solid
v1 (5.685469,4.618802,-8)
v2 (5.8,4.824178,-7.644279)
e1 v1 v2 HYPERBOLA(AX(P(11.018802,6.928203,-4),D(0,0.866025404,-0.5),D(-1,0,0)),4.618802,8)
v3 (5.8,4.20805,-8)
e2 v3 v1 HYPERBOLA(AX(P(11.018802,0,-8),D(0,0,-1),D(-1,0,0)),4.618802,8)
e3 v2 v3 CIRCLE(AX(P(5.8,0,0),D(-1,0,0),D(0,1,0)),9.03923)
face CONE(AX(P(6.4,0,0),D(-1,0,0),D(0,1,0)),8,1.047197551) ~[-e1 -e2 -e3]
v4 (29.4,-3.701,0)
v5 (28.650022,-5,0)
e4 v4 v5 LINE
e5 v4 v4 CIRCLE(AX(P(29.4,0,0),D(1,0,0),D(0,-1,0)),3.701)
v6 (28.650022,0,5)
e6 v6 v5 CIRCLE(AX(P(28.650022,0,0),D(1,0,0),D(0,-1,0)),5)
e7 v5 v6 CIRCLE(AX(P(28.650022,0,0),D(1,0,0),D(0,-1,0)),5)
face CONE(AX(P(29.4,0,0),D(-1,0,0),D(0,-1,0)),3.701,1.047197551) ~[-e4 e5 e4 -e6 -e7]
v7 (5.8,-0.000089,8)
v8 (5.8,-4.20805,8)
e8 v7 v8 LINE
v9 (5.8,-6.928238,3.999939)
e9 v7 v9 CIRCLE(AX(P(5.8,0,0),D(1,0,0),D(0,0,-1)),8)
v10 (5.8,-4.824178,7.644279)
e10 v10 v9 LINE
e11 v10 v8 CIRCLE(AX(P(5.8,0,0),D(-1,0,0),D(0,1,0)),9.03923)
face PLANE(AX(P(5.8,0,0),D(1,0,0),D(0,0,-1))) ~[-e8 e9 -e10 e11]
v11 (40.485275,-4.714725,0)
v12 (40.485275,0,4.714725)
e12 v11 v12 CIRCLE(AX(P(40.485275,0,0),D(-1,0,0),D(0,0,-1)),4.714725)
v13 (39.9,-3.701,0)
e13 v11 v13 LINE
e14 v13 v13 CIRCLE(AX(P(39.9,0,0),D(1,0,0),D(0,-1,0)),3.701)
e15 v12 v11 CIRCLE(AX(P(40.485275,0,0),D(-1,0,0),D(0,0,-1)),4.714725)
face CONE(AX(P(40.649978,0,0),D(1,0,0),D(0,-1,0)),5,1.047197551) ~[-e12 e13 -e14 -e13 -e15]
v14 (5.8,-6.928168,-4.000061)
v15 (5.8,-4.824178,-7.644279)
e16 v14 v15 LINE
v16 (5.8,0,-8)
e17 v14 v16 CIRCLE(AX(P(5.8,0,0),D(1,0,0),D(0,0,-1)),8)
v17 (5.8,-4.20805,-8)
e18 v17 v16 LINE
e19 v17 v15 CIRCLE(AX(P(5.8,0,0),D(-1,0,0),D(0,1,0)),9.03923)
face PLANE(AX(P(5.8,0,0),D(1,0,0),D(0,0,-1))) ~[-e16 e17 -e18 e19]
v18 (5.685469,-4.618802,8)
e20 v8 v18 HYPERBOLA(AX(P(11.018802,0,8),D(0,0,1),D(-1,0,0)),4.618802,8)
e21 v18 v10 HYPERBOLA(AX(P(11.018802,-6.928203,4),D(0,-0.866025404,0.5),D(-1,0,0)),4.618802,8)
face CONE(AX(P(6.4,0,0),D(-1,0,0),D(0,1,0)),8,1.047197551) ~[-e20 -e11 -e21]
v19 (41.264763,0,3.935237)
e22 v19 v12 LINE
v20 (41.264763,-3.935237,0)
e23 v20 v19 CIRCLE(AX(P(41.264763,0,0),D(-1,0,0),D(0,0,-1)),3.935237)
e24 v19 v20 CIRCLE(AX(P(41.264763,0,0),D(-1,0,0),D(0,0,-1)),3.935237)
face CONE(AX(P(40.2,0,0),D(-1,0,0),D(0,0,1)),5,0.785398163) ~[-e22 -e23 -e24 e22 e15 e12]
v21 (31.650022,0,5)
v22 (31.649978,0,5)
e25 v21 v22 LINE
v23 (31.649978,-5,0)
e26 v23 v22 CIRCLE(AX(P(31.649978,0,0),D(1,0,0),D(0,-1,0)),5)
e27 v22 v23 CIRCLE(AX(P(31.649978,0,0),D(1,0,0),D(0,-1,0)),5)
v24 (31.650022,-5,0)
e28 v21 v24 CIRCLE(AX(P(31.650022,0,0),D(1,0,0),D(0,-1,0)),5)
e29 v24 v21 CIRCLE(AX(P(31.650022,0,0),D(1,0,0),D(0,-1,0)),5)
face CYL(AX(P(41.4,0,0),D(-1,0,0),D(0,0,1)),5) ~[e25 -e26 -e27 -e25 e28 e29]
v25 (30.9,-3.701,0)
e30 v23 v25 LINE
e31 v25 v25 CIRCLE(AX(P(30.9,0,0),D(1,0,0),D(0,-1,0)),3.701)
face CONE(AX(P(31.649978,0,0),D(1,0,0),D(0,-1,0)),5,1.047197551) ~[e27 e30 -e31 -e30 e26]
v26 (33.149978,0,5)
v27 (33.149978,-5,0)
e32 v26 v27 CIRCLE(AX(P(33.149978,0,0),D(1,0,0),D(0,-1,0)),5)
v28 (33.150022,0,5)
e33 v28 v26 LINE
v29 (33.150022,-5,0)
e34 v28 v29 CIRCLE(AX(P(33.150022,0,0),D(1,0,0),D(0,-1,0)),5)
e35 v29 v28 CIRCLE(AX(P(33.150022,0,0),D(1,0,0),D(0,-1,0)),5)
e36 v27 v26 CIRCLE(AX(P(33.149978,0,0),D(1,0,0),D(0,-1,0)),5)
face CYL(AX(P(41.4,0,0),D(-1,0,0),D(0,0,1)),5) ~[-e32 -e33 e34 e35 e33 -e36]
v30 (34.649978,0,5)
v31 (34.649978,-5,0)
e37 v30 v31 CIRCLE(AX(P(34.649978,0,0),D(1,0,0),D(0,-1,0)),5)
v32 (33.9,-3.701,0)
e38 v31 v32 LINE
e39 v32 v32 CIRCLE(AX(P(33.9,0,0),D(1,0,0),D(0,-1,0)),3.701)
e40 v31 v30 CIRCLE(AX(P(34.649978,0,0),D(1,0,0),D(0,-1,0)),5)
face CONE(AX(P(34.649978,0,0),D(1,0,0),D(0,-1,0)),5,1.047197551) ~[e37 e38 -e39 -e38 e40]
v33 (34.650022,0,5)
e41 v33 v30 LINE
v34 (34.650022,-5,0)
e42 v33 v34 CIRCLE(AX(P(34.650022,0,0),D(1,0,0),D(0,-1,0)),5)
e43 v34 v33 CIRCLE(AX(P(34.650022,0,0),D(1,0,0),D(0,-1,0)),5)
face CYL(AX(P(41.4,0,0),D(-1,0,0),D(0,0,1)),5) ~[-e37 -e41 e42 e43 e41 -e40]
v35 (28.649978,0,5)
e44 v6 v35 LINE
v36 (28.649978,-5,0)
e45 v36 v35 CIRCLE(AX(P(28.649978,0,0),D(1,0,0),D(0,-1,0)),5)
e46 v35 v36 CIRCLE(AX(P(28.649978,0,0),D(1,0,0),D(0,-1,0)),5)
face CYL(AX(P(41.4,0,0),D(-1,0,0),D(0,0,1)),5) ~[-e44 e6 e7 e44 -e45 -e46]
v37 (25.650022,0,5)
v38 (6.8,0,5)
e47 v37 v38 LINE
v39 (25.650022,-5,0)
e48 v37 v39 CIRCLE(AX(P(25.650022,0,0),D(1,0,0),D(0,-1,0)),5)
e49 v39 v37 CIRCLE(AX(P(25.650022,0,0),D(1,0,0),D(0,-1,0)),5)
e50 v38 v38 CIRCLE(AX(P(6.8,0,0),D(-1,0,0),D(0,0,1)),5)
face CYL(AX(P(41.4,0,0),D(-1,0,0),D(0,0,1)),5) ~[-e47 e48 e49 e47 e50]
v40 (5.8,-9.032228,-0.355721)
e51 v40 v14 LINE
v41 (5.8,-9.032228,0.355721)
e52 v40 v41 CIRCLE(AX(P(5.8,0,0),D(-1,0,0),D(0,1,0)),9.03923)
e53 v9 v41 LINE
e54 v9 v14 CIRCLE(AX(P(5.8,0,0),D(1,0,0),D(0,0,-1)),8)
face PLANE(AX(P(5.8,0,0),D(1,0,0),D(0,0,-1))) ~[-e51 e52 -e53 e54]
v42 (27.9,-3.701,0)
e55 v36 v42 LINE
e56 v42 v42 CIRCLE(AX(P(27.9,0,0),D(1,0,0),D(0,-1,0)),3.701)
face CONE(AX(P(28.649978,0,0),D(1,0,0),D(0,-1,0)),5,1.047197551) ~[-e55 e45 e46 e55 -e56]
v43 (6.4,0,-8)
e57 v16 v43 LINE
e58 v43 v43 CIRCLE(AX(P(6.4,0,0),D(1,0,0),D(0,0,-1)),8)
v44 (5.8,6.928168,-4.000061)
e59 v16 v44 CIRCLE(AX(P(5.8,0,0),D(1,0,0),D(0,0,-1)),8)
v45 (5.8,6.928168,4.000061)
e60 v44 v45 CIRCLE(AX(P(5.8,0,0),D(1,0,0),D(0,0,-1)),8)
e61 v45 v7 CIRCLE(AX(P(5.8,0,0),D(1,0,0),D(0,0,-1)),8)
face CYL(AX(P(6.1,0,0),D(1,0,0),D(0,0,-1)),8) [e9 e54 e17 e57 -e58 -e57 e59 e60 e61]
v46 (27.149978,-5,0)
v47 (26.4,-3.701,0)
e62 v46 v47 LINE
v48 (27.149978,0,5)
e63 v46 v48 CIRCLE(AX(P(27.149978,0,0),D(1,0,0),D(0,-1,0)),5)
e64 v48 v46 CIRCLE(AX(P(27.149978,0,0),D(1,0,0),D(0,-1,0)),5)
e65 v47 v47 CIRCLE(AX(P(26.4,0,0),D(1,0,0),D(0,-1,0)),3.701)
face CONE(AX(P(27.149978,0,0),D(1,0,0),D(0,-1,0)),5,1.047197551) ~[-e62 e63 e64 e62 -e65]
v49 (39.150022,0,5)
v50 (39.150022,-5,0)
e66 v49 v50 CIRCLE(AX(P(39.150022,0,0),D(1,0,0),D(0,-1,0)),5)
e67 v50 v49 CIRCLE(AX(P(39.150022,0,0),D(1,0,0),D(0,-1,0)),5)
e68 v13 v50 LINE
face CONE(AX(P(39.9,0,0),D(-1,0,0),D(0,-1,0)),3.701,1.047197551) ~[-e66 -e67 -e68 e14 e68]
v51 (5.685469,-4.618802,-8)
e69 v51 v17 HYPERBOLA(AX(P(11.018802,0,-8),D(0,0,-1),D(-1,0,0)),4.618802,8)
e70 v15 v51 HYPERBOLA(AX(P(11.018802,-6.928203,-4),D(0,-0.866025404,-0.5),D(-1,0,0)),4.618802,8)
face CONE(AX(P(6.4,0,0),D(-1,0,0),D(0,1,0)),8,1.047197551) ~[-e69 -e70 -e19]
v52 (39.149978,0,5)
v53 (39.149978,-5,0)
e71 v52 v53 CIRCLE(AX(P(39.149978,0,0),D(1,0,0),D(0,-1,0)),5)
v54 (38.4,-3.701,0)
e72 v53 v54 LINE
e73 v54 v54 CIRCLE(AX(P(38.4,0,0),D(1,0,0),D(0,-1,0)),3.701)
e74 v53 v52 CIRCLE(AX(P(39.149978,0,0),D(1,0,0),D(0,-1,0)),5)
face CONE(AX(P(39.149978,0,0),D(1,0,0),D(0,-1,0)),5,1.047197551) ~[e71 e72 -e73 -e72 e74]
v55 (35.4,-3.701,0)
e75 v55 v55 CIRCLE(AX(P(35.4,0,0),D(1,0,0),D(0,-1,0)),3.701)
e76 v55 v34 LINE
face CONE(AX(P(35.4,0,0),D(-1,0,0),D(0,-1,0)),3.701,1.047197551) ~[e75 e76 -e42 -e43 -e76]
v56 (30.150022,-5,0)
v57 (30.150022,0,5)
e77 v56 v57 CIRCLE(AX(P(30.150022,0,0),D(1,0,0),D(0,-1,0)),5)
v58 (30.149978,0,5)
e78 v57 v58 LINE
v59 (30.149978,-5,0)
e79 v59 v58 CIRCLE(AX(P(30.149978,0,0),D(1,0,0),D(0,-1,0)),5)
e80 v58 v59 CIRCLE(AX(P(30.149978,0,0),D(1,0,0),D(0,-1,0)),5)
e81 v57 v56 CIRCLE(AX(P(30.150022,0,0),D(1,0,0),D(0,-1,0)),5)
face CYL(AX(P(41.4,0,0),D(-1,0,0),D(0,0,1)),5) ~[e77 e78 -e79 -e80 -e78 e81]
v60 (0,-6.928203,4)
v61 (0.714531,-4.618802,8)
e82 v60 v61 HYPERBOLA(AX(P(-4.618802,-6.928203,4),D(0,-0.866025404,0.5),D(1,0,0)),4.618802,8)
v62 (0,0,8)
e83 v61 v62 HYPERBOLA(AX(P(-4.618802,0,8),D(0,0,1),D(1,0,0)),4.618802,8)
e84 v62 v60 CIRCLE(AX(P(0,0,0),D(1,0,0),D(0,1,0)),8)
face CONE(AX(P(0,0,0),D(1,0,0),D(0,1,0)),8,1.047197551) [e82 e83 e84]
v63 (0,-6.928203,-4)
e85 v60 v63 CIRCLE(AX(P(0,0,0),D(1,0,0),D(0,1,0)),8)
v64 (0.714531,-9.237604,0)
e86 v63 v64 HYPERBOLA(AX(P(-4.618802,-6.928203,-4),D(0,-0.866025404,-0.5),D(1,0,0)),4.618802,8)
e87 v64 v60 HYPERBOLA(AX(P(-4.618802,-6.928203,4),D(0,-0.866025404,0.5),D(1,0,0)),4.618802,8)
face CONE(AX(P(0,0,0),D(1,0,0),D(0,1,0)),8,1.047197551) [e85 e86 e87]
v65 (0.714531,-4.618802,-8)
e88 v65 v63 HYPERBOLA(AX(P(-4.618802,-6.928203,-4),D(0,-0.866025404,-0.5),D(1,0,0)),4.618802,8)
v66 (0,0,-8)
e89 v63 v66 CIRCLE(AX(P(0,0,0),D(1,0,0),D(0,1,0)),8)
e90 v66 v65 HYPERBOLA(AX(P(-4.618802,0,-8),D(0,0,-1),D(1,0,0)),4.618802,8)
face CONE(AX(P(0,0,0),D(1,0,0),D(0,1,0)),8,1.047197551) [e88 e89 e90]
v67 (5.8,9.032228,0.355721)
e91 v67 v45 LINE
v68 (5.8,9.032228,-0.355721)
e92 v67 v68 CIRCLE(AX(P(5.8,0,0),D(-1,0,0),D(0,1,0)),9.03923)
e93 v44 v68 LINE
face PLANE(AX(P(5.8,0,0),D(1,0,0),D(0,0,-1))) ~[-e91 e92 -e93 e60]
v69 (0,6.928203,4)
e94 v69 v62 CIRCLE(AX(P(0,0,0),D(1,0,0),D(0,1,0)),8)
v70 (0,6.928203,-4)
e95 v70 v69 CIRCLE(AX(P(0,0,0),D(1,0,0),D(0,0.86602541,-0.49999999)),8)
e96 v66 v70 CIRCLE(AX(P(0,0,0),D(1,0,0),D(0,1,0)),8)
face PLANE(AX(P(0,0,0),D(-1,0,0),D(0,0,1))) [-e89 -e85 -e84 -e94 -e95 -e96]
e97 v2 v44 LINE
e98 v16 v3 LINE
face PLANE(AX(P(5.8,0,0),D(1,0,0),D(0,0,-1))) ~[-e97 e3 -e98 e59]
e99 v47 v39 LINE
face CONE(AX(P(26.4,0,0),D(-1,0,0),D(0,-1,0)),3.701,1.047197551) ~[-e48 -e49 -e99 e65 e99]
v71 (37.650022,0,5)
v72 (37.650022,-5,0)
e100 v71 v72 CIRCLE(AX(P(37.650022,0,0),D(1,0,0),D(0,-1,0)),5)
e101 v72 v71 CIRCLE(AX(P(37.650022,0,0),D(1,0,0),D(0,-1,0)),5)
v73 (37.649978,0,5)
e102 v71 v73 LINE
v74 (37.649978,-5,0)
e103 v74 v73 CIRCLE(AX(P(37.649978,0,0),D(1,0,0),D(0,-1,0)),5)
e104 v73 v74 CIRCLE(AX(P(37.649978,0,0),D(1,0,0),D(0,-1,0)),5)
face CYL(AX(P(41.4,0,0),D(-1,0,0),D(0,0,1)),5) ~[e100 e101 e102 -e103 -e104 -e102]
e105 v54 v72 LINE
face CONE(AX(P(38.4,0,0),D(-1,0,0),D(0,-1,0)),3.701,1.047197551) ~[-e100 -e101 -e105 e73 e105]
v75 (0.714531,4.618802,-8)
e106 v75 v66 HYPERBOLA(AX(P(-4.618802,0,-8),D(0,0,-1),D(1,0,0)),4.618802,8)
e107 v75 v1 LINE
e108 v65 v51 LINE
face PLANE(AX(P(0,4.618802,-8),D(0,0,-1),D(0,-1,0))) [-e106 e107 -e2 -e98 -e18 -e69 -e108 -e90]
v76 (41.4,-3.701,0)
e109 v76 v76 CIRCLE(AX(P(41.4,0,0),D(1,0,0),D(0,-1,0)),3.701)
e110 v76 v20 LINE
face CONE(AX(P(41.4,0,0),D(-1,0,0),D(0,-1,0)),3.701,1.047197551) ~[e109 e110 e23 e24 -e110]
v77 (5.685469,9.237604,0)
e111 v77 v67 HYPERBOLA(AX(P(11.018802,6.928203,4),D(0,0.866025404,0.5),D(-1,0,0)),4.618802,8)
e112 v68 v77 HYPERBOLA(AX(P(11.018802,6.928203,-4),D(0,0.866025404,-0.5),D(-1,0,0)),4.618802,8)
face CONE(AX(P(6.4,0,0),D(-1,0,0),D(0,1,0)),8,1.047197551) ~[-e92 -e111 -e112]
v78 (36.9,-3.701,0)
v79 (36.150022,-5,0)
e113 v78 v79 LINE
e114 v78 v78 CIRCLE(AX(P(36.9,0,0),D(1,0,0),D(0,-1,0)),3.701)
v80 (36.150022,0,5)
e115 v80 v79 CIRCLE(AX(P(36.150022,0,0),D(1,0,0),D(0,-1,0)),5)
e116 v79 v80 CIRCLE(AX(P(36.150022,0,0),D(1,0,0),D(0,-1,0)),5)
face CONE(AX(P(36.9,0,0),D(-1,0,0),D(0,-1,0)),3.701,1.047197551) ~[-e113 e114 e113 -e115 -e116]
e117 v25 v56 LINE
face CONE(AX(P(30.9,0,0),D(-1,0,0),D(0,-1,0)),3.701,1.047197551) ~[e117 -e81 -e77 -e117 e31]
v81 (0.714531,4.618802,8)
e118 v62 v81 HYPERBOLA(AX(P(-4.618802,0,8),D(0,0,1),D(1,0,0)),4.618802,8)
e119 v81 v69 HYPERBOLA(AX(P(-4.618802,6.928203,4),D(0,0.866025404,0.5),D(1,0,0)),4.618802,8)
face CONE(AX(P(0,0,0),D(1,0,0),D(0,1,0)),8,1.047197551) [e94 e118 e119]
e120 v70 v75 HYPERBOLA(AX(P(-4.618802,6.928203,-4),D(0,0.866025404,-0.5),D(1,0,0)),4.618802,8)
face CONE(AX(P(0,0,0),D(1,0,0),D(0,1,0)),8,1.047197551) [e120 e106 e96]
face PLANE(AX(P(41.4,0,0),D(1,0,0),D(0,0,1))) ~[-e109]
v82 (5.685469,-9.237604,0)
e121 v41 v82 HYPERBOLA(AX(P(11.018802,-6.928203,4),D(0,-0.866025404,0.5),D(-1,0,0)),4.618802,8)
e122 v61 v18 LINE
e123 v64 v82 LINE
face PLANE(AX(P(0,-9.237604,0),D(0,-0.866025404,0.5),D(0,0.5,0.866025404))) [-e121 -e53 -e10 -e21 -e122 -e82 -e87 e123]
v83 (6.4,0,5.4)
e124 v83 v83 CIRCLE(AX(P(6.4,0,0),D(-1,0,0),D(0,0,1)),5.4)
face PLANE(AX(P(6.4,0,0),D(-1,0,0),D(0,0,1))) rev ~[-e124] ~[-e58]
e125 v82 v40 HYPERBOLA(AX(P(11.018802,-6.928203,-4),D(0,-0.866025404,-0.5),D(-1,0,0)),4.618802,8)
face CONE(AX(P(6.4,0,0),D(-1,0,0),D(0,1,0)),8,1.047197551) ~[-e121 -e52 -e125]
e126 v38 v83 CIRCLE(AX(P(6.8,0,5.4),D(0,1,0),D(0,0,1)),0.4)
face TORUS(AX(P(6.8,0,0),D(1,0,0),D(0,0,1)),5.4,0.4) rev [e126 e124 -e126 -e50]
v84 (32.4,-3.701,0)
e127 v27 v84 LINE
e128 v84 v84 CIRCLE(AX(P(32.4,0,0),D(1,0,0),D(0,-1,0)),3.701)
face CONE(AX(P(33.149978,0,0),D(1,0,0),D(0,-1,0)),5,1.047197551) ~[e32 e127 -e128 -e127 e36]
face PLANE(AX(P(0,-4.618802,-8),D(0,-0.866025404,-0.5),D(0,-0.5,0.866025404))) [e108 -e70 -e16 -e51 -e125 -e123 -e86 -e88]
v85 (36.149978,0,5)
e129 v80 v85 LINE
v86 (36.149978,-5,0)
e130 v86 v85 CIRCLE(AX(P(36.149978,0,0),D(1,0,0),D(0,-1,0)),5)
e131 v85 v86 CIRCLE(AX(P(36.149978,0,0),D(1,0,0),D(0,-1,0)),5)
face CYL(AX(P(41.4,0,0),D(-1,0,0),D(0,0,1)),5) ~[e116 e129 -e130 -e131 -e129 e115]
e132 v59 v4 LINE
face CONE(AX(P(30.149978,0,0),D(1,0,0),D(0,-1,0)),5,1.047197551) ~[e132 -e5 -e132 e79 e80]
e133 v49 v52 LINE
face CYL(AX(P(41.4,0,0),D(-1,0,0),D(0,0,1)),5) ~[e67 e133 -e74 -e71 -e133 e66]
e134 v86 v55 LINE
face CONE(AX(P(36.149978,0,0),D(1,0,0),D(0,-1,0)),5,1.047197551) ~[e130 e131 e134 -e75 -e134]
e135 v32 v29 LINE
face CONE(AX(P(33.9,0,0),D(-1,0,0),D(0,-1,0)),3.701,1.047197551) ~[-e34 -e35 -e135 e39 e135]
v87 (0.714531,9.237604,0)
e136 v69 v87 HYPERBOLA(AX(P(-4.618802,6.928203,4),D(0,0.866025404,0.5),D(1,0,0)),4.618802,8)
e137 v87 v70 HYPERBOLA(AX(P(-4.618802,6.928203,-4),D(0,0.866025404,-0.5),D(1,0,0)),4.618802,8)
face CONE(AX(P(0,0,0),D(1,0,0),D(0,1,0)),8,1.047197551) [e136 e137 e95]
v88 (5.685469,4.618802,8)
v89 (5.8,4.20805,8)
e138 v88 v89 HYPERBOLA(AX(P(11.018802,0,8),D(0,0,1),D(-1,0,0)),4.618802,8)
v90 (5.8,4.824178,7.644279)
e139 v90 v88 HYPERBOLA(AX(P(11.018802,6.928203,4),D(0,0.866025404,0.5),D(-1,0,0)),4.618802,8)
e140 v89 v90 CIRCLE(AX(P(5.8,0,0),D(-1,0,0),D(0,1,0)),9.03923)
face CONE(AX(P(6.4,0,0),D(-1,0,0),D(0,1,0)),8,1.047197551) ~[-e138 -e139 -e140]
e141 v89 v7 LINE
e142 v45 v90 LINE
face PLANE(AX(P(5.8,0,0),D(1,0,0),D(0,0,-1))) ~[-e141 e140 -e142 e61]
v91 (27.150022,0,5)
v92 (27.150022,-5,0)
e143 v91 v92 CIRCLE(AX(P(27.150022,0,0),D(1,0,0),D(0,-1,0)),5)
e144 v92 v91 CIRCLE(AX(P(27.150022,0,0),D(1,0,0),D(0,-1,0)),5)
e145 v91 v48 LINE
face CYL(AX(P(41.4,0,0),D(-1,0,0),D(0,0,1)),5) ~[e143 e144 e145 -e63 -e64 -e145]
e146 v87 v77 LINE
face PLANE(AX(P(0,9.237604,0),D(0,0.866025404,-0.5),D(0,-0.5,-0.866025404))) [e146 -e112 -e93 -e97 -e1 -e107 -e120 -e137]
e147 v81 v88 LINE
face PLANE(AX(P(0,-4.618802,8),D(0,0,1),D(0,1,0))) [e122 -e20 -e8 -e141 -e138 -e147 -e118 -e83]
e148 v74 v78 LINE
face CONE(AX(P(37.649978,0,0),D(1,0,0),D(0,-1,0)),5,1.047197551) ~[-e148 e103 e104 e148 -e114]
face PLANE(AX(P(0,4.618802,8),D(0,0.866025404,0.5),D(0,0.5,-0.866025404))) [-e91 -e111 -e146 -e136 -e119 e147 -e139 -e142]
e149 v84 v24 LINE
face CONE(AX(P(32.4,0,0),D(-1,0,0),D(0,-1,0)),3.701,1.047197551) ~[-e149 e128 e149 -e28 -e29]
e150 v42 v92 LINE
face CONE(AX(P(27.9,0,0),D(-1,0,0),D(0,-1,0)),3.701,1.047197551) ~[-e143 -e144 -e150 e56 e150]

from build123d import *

# Parameters (mm, degrees)
EXTRUDE_378_DEPTH      = 6.4
SKETCH_4_W             = 0.6
SKETCH_4_H             = 11.237604307
CHAMFER_2060_SIZE      = 1.2
FILLET_2105_R          = 0.4
PATTERN_LINEAR_1_COUNT = 11
PATTERN_LINEAR_1_PITCH = 1.5


with BuildPart() as part:
    # 草图1 → Extrude 378 (new body)
    with BuildSketch(Plane(origin=(0, 0, 0), x_dir=(0, 0, -1), z_dir=(1, 0, 0))):
        Polygon((8, 4.618802154), (8, -4.618802154), (0, -9.237604307), (-8, -4.618802154), (-8, 4.618802154), (0, 9.237604307), align=None)
    extrude(amount=EXTRUDE_378_DEPTH)

    # 草图2 → 凸台-旋转1 (revolve)
    with BuildSketch(Plane.XY, mode=Mode.PRIVATE) as revolve_1_sk:
        Polygon((0, 0), (41.4, 0), (41.4, 3.701), (41.4, 5), (7.791693541, 5), (0, 5), align=None)
    revolve(revolve_1_sk.sketch.rotate(Axis((0, 0, 0), (1, 0, 0)), 90), axis=Axis((0, 0, 0), (1, 0, 0)))

    # 草图3 → 切除-旋转1 (revolve, cut)
    with BuildSketch(Plane.XY):
        Polygon((0, 8), (3.601282526, 14.237604307), (3.601282526, 19.237604307), (-10, 19.237604307), (-10, 8), align=None)
    revolve(axis=Axis((0, 0, 0), (1, 0, 0)), mode=Mode.SUBTRACT)

    # 草图5 → 切除-旋转2 (revolve, cut)
    with BuildSketch(Plane.XY):
        Polygon((6.4, 8), (2.798717474, 14.237604307), (2.798717474, 19.237604307), (12.798717474, 19.237604307), (12.798717474, 8), align=None)
    revolve(axis=Axis((0, 0, 0), (1, 0, 0)), mode=Mode.SUBTRACT)

    # 草图4 → 切除-旋转3 (revolve, cut)
    with BuildSketch(Plane.XY, mode=Mode.PRIVATE) as cut_revolve_3_sk:
        with Locations((6.1, 13.618802154)):
            Rectangle(SKETCH_4_W, SKETCH_4_H)
    revolve(cut_revolve_3_sk.sketch.rotate(Axis((0, 0, 0), (1, 0, 0)), 270), axis=Axis((0, 0, 0), (1, 0, 0)), mode=Mode.SUBTRACT)

    # Chamfer 2060
    chamfer_2060_edges = [part.edges().sort_by_distance(p)[0] for p in [
        (41.4, 0, -5),
    ]]
    chamfer(chamfer_2060_edges, length=CHAMFER_2060_SIZE)

    # Fillet 2105
    fillet_2105_edges = [part.edges().sort_by_distance(p)[0] for p in [
        (6.4, 0, -5),
    ]]
    fillet(fillet_2105_edges, radius=FILLET_2105_R)

    # 草图6 → 切除-旋转4 (revolve, cut)
    with BuildSketch(Plane.XY):
        Polygon((26.4, -3.701), (25.650022, -5), (25.650022, -6.25), (27.149978, -6.25), (27.149978, -5), align=None)
    cut_revolve_4 = revolve(axis=Axis((-3.175, 0, 0), (1, 0, 0)), mode=Mode.SUBTRACT)

    # 阵列(线性)1: 切除-旋转4 ×11
    with Locations(*[(i * PATTERN_LINEAR_1_PITCH, 0, 0) for i in range(1, PATTERN_LINEAR_1_COUNT)]):
        add(cut_revolve_4, mode=Mode.SUBTRACT)


solid = part.part
